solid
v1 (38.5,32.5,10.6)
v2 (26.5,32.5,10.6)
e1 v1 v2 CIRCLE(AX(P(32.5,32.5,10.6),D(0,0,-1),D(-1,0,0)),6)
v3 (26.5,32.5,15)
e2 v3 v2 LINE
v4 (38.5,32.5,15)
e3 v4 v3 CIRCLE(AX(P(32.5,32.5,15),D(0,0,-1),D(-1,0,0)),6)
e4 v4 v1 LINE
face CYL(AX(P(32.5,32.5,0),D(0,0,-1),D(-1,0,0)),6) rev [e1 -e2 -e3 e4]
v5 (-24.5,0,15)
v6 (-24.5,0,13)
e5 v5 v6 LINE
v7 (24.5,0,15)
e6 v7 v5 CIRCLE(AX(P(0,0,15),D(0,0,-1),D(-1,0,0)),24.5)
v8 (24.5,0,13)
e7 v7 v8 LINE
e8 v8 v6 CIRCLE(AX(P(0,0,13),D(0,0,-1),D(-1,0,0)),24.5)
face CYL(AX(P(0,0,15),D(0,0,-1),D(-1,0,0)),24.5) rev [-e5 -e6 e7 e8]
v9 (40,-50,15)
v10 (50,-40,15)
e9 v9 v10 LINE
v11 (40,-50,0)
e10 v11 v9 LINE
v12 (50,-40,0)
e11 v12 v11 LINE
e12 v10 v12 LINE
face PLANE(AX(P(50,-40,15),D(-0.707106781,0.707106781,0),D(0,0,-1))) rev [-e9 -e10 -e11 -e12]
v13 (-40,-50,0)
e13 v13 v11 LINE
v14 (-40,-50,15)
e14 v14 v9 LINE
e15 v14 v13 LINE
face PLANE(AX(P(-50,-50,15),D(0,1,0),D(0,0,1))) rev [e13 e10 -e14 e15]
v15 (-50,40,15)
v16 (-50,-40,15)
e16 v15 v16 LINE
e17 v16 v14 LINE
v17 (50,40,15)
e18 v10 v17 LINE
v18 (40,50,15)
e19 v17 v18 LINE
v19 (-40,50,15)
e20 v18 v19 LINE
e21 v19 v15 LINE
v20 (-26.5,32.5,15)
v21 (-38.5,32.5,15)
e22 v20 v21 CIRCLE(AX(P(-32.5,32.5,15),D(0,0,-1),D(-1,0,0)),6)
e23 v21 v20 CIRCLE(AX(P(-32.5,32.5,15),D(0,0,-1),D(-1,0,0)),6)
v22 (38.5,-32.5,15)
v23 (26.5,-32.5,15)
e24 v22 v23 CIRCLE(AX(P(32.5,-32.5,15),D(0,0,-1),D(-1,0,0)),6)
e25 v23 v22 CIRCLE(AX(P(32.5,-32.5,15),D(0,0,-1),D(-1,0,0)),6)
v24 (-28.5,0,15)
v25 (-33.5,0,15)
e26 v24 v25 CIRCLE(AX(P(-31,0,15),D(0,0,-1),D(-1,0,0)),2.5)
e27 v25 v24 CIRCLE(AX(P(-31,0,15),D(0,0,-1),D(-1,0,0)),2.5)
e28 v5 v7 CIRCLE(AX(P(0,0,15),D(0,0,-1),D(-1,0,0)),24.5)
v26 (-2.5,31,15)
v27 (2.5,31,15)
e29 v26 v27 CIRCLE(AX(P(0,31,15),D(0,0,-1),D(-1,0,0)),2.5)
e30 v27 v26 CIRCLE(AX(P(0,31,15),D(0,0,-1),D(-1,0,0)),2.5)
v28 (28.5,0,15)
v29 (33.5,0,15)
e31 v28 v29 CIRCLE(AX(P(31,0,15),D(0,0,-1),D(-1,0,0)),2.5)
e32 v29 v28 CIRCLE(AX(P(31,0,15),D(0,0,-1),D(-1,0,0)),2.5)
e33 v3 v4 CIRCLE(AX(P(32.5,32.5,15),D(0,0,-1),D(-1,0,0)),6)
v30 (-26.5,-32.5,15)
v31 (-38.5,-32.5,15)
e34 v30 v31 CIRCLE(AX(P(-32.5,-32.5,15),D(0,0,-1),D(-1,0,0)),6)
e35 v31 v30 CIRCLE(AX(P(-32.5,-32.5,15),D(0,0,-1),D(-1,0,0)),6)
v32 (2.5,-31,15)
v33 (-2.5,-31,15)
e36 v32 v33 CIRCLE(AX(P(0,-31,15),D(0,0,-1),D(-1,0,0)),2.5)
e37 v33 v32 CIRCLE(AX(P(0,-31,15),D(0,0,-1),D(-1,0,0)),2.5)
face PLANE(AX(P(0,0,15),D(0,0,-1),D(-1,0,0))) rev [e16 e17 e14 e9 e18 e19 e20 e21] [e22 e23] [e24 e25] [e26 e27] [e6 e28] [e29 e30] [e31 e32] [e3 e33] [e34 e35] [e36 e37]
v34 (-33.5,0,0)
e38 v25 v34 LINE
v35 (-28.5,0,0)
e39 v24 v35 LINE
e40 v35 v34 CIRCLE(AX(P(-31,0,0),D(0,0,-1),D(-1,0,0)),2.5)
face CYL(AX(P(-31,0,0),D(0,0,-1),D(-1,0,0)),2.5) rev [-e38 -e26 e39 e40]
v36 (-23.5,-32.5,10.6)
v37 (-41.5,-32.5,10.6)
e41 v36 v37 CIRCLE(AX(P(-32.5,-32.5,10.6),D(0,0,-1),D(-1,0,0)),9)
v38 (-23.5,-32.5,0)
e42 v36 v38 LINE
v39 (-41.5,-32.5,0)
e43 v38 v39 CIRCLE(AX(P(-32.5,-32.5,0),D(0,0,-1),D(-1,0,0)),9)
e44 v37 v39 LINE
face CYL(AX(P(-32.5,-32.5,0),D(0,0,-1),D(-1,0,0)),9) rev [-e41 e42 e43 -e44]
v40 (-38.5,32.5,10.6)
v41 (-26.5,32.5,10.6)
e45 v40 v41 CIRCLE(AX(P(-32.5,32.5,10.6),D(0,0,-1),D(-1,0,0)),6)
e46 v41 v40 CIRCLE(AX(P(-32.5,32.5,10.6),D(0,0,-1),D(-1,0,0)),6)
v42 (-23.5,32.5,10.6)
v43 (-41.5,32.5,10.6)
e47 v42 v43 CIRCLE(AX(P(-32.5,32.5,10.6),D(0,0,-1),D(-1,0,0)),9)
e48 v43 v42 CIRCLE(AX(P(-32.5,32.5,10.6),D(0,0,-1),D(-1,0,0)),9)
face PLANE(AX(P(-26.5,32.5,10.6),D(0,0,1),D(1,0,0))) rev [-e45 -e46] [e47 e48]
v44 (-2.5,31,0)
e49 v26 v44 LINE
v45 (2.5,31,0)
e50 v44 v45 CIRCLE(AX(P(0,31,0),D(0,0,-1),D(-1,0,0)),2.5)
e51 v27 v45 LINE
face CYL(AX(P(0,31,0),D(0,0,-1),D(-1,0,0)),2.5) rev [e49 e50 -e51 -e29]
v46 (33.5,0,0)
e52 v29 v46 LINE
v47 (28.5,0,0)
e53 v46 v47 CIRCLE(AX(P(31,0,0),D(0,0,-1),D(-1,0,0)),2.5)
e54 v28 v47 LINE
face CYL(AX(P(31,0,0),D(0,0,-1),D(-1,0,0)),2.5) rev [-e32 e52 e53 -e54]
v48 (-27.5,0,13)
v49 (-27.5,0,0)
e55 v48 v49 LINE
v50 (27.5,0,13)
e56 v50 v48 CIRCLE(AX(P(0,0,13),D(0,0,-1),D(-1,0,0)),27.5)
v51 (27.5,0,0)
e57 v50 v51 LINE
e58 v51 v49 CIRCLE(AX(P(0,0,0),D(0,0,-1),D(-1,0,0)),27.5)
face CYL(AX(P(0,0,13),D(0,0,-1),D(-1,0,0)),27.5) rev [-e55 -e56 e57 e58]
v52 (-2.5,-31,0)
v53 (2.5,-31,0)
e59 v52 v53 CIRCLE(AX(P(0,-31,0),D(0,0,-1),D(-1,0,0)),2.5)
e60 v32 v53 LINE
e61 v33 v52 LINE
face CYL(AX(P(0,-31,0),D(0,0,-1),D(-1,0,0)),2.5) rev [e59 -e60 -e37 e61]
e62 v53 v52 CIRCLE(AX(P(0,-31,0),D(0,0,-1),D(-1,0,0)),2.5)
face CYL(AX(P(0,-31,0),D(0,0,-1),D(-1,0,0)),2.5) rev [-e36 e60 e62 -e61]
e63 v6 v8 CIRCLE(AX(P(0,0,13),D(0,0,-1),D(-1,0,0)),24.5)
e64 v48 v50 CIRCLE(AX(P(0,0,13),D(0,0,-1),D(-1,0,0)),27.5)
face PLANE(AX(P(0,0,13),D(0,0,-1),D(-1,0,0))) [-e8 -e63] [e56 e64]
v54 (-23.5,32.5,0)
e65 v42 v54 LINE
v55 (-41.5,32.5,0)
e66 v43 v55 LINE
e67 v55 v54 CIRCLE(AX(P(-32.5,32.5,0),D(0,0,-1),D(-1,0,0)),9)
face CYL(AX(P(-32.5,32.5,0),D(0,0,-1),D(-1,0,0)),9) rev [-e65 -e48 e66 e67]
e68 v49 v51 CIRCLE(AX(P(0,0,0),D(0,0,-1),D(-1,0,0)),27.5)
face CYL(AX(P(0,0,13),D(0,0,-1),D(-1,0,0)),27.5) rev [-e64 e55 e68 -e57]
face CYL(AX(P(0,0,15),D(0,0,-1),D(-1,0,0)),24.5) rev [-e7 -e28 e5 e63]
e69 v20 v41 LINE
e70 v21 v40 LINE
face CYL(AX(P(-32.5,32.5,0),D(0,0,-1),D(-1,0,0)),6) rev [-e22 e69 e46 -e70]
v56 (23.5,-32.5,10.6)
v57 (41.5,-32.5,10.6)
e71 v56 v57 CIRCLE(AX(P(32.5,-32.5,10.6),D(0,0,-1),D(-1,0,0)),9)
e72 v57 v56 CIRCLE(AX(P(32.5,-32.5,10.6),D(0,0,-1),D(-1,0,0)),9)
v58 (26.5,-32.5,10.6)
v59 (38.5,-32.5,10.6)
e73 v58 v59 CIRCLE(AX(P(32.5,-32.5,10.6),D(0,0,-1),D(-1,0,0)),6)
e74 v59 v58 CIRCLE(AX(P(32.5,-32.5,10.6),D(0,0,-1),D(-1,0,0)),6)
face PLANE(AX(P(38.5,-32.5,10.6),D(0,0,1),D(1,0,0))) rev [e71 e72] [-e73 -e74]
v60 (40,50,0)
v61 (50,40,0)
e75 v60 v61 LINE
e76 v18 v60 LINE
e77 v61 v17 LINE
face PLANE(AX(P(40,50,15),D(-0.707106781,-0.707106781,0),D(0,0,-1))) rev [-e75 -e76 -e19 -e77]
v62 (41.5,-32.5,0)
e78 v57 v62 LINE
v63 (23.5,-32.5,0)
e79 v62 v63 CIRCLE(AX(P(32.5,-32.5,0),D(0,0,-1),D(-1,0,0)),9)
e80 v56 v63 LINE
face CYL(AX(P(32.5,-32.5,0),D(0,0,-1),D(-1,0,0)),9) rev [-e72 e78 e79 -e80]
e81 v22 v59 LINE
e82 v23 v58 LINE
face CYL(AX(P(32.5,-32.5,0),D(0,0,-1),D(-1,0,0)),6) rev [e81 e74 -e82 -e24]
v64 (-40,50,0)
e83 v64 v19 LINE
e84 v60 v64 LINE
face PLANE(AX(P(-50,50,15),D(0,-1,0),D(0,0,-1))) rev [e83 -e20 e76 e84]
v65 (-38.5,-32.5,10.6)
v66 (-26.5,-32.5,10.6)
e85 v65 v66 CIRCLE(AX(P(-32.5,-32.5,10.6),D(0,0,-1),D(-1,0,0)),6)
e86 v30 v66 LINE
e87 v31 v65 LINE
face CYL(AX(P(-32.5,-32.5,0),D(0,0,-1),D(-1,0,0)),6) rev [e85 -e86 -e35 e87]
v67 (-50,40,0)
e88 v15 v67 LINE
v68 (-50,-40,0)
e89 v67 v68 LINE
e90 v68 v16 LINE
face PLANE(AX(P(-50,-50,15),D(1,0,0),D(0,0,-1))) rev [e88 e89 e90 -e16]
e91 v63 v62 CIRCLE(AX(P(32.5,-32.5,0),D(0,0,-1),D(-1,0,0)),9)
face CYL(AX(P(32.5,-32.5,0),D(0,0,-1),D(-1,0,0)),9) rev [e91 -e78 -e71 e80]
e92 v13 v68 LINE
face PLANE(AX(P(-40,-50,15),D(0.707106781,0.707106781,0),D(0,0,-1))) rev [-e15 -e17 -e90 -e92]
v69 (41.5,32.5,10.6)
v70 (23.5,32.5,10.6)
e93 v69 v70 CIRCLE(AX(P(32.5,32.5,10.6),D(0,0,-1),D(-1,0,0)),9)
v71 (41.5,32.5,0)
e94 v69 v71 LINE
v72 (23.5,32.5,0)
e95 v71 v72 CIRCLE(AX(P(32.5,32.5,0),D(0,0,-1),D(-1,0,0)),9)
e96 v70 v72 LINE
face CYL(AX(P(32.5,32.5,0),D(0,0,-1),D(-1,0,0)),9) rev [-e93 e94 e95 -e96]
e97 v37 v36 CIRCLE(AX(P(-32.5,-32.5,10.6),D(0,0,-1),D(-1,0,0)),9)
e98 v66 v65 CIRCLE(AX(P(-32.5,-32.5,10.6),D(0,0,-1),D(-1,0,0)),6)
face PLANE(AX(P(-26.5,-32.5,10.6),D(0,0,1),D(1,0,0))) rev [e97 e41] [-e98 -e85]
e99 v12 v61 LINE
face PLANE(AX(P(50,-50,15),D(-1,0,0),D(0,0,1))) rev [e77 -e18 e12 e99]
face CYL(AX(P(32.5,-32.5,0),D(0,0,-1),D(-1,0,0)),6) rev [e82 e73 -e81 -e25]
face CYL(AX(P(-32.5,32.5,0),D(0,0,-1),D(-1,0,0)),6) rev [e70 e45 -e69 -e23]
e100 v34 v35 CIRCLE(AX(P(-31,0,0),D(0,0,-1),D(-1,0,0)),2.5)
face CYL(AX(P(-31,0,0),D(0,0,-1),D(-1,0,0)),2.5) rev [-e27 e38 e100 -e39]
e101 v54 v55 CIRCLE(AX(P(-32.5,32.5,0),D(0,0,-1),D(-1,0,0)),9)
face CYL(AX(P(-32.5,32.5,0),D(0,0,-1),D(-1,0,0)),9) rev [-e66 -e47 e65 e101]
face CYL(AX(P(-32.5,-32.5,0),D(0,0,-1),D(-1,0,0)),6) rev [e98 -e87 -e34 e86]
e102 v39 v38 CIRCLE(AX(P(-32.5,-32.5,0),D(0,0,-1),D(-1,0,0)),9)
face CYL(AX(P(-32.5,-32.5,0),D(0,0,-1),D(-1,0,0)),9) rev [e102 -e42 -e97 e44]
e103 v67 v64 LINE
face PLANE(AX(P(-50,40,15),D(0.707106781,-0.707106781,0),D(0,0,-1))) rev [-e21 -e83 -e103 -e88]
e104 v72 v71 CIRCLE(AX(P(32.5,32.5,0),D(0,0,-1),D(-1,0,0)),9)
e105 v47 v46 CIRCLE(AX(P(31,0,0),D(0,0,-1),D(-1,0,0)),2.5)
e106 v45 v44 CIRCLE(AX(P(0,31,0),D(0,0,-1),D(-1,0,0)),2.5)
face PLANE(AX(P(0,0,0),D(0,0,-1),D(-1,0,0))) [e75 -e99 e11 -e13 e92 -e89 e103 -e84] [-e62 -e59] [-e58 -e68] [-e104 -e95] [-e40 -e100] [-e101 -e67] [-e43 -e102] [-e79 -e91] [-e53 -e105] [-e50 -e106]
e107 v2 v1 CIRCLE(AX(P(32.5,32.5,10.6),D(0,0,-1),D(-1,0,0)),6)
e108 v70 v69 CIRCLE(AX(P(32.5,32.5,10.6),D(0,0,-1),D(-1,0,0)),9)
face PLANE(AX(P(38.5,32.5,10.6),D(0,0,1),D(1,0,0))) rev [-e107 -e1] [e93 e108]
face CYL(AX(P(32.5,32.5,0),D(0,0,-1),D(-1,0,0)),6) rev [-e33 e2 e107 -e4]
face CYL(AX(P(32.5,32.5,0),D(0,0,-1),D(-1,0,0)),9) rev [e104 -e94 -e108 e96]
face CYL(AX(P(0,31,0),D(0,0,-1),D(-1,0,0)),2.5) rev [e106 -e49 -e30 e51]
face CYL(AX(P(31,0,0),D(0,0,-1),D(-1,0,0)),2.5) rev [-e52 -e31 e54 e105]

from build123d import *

# Parameters (mm, degrees)
SKETCH_1_W                    = 100
SKETCH_1_H                    = 100
EXTRUDE_1_DEPTH               = 15
HOLE_WIZARD_M10_1_D           = 12
HOLE_WIZARD_M10_1_CBORE_D     = 18
HOLE_WIZARD_M10_1_CBORE_DEPTH = 10.6
CHAMFER_1_SIZE                = 10
SKETCH_11_R                   = 27.5
CUT_EXTRUDE_4_DEPTH           = 13
HOLE_WIZARD_M6_1_D            = 5
HOLE_WIZARD_M6_1_DEPTH        = 15
HOLE_WIZARD_M6_1_TIP          = 1.502151548
SKETCH_14_R                   = 24.5
CUT_EXTRUDE_5_DEPTH           = 72.895757872


with BuildPart() as part:
    # 草图1 → 凸台-拉伸1 (new body)
    with BuildSketch(Plane.XY):
        Rectangle(SKETCH_1_W, SKETCH_1_H)
    extrude(amount=EXTRUDE_1_DEPTH)

    # M10 六角凹头螺钉的柱形沉头孔1 (through all)
    with Locations(Plane(origin=(0, 0, 0), x_dir=(-1, 0, 0), z_dir=(0, 0, -1))):
        with Locations((-32.5, 32.5), (32.5, 32.5), (32.5, -32.5), (-32.5, -32.5)):
            CounterBoreHole(HOLE_WIZARD_M10_1_D / 2, HOLE_WIZARD_M10_1_CBORE_D / 2, HOLE_WIZARD_M10_1_CBORE_DEPTH)

    # 倒角1
    chamfer_1_edges = [part.edges().sort_by_distance(p)[0] for p in [
        (50, -50, 7.5),
        (-50, -50, 7.5),
        (-50, 50, 7.5),
        (50, 50, 7.5),
    ]]
    chamfer(chamfer_1_edges, length=CHAMFER_1_SIZE)

    # 草图11 → 切除-拉伸4 (cut)
    with BuildSketch(Plane(origin=(0, 0, 0), x_dir=(-1, 0, 0), z_dir=(0, 0, -1))):
        Circle(SKETCH_11_R)
    extrude(amount=-CUT_EXTRUDE_4_DEPTH, mode=Mode.SUBTRACT)

    # M6 螺纹孔1
    with Locations(Plane(origin=(0, 0, 0), x_dir=(-1, 0, 0), z_dir=(0, 0, -1))):
        with Locations((0, 31), (31, 0), (0, -31), (-31, 0)):
            Hole(HOLE_WIZARD_M6_1_D / 2, depth=HOLE_WIZARD_M6_1_DEPTH)
            with Locations((0, 0, -(HOLE_WIZARD_M6_1_DEPTH + HOLE_WIZARD_M6_1_TIP / 2))):  # 118° drill point
                Cone(0, HOLE_WIZARD_M6_1_D / 2, HOLE_WIZARD_M6_1_TIP, mode=Mode.SUBTRACT)

    # 草图14 → 切除-拉伸5 (cut, through all)
    with BuildSketch(Plane(origin=(0, 0, 13), x_dir=(-1, 0, 0), z_dir=(0, 0, -1))):
        Circle(SKETCH_14_R)
    extrude(amount=-CUT_EXTRUDE_5_DEPTH, mode=Mode.SUBTRACT)


solid = part.part
